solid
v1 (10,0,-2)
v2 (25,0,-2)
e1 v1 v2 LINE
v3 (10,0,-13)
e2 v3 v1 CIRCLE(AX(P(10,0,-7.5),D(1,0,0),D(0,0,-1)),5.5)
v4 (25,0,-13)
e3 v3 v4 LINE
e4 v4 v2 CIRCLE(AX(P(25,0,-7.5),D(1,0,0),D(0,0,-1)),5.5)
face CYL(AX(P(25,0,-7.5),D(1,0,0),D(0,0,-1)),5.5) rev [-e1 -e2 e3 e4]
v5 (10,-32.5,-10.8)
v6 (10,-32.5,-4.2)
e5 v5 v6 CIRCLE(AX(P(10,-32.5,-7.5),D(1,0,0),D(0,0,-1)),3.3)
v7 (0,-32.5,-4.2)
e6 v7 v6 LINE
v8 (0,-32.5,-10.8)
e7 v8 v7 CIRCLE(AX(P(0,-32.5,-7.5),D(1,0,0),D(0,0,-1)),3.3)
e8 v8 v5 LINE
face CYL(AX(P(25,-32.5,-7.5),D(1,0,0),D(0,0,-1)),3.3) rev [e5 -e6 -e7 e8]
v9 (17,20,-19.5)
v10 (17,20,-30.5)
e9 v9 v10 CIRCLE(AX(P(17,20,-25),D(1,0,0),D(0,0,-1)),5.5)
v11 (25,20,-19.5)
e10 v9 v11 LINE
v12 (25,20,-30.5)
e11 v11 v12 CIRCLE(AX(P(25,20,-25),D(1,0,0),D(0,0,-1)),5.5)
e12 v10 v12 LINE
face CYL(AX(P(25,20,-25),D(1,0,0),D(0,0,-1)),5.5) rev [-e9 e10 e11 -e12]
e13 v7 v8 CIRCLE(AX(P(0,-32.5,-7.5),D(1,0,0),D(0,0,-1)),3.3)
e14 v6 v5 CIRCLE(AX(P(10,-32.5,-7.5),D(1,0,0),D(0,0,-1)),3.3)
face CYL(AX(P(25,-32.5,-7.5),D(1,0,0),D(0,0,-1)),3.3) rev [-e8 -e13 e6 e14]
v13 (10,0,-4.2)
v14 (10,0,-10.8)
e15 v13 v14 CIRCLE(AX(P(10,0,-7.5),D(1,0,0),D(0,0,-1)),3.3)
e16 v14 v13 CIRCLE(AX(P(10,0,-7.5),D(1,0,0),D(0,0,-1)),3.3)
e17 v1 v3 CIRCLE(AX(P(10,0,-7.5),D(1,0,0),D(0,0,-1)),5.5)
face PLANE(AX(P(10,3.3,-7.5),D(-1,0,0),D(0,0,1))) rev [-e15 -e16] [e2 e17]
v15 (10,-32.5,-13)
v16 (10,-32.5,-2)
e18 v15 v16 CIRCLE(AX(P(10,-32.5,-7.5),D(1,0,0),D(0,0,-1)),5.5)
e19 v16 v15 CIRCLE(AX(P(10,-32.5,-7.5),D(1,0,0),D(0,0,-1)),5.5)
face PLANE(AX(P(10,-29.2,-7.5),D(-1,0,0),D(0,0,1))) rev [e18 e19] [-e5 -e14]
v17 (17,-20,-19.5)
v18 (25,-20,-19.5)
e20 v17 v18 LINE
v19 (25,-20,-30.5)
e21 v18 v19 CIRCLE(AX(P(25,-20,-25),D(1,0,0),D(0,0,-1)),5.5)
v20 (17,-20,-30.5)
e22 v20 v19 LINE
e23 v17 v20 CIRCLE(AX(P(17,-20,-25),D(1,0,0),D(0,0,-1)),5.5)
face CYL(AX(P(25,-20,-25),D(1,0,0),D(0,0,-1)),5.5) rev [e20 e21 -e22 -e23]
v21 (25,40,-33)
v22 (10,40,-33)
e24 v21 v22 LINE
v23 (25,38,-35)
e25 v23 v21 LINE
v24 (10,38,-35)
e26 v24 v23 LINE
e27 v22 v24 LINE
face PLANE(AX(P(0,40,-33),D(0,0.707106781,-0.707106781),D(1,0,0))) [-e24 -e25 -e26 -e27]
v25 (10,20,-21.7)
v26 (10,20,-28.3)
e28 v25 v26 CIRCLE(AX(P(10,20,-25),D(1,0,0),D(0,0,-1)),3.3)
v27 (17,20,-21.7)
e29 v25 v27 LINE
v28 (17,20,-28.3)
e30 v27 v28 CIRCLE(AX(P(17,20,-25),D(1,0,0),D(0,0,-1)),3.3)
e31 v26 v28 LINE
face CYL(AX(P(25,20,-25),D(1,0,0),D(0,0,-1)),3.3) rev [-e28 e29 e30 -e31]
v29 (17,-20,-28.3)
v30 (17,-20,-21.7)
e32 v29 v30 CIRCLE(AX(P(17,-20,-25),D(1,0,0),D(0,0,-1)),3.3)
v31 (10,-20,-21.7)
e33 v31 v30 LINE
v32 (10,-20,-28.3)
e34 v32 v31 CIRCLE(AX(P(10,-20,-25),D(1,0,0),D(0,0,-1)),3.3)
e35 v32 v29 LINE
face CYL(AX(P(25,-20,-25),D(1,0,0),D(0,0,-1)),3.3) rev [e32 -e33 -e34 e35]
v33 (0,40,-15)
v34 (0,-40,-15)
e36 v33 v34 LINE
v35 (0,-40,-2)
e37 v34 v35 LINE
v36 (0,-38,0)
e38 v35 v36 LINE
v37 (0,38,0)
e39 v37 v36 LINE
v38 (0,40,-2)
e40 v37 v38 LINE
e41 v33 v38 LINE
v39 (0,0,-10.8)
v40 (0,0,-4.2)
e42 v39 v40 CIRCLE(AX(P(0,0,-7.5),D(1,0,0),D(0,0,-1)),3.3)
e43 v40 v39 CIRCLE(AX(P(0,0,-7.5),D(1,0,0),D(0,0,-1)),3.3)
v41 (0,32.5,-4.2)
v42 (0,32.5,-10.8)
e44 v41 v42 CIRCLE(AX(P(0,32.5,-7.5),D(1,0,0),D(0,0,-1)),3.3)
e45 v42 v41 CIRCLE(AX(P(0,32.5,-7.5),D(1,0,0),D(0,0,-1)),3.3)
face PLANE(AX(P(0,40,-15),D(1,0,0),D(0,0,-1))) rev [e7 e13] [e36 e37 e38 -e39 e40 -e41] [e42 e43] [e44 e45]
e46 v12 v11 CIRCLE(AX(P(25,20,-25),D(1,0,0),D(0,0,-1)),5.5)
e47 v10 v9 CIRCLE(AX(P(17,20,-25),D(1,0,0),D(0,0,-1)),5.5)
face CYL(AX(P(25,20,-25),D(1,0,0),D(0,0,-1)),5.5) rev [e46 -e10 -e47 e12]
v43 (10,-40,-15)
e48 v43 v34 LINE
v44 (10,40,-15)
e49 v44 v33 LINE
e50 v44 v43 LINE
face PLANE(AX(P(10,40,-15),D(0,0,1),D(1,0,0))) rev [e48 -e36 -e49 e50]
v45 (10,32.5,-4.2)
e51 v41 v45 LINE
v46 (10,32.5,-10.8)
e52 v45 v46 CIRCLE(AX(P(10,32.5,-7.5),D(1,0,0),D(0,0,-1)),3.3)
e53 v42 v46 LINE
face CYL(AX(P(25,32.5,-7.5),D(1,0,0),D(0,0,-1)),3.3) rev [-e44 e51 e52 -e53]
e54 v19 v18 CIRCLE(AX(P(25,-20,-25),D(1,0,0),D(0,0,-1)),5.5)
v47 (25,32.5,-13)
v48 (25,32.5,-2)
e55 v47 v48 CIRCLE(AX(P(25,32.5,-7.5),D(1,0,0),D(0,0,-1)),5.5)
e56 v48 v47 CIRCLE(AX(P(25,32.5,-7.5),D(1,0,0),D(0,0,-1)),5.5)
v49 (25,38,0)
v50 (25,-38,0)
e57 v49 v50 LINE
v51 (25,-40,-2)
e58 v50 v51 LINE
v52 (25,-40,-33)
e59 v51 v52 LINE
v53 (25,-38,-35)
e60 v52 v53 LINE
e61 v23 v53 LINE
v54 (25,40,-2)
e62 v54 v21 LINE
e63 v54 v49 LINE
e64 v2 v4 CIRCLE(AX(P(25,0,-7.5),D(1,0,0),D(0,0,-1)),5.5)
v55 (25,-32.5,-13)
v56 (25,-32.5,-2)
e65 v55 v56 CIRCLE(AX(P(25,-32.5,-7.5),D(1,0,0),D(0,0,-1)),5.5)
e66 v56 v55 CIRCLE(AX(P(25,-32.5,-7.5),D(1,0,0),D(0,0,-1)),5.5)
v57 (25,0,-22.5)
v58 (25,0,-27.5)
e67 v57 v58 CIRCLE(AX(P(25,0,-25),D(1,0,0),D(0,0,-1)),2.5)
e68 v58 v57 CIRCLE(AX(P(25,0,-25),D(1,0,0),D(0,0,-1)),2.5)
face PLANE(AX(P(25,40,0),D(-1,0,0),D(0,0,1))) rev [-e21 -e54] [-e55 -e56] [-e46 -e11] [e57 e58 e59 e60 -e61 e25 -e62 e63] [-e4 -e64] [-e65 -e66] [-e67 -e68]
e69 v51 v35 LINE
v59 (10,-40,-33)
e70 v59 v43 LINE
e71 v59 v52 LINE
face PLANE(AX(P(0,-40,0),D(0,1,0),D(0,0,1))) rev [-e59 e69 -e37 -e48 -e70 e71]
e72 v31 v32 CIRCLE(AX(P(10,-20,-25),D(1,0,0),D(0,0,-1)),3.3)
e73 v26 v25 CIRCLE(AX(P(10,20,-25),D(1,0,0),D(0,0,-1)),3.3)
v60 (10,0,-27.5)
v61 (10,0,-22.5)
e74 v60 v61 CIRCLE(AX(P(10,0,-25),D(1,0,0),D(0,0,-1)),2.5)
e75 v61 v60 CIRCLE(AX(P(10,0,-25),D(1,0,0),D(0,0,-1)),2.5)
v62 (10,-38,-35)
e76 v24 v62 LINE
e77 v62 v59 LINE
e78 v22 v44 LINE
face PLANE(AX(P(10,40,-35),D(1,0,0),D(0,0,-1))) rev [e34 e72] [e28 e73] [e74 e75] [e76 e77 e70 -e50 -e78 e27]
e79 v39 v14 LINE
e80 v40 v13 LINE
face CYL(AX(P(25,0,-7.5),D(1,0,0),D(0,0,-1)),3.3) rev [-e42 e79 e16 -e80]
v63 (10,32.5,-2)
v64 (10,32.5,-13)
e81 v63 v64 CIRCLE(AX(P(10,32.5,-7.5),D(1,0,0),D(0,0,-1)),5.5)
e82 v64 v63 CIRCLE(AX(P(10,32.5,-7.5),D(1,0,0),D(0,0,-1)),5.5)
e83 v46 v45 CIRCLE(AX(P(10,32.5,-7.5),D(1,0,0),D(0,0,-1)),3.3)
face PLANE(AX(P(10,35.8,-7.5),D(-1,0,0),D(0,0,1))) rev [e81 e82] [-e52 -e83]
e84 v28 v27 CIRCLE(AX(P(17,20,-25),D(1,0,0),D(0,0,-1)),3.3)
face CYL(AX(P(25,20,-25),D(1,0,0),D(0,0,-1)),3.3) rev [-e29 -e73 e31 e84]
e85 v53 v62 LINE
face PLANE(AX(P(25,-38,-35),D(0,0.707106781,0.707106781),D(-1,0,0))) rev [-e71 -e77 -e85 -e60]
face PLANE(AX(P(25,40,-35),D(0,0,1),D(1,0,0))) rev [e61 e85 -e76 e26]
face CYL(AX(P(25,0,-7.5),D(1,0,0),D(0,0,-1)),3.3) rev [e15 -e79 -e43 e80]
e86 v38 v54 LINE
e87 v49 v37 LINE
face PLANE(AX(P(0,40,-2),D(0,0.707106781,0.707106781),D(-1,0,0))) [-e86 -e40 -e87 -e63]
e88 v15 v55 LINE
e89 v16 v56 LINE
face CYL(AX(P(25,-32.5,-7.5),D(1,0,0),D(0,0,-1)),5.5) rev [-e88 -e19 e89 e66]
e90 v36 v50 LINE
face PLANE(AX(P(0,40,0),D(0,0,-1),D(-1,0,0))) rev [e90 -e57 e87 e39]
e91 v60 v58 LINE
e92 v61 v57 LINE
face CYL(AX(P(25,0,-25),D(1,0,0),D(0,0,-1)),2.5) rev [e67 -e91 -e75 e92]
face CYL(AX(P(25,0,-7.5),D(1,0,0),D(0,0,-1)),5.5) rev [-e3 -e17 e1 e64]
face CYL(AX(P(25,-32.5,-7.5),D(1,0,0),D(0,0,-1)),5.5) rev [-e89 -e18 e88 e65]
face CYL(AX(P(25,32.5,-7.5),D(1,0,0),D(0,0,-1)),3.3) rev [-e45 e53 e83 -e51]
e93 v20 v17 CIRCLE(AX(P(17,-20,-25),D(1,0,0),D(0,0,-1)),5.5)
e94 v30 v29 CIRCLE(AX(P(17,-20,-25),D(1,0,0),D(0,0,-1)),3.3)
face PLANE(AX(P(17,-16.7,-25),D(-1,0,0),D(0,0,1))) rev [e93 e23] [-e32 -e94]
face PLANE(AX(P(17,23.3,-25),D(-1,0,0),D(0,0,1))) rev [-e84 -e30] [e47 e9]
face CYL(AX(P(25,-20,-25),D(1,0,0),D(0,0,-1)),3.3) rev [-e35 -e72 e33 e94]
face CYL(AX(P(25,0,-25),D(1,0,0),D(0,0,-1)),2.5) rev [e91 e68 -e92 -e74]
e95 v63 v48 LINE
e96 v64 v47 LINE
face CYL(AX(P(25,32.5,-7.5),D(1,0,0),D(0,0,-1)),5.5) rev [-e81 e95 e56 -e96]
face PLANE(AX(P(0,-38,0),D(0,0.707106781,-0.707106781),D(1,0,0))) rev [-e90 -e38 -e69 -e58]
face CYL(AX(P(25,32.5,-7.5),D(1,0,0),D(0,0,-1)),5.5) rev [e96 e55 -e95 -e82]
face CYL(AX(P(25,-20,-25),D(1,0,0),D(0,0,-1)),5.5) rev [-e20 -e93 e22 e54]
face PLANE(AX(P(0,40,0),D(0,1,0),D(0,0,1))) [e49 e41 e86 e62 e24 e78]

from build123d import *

# Parameters (mm, degrees)
EXTRUDE_1_DEPTH              = 40
CHAMFER_1_SIZE               = 2
HOLE_WIZARD_M6_1_D           = 6.6
HOLE_WIZARD_M6_1_CBORE_D     = 11
HOLE_WIZARD_M6_1_CBORE_DEPTH = 15
HOLE_WIZARD_M6_1_2_D         = 5
HOLE_WIZARD_M6_2_D           = 6.6
HOLE_WIZARD_M6_2_CBORE_D     = 11
HOLE_WIZARD_M6_2_CBORE_DEPTH = 8


with BuildPart() as part:
    # 草图1 → 凸台-拉伸1 (new, symmetric)
    with BuildSketch(Plane(origin=(0, 0, 0), x_dir=(1, 0, 0), z_dir=(0, 1, 0))):
        Polygon((0, 0), (25, 0), (25, 35), (10, 35), (10, 15), (0, 15), align=None)
    extrude(amount=EXTRUDE_1_DEPTH, both=True)

    # 倒角1
    chamfer_1_edges = [part.edges().sort_by_distance(p)[0] for p in [
        (17.5, 40, -35),
        (17.5, -40, -35),
        (12.5, -40, 0),
        (12.5, 40, 0),
    ]]
    chamfer(chamfer_1_edges, length=CHAMFER_1_SIZE)

    # Hole Wizard M6 _1 (through all)
    with Locations(Plane(origin=(25, 0, 0), x_dir=(0, 0, -1), z_dir=(1, 0, 0))):
        with Locations((7.5, 32.5), (7.5, 0), (7.5, -32.5)):
            CounterBoreHole(HOLE_WIZARD_M6_1_D / 2, HOLE_WIZARD_M6_1_CBORE_D / 2, HOLE_WIZARD_M6_1_CBORE_DEPTH)

    # Hole Wizard M6 _1 2 (through all)
    with Locations(Plane(origin=(25, 0, 0), x_dir=(0, 0, -1), z_dir=(1, 0, 0))):
        with Locations((25, 0)):
            Hole(HOLE_WIZARD_M6_1_2_D / 2)

    # M6 六角圆柱头螺钉的柱形沉头孔2 (through all)
    with Locations(Plane(origin=(25, 0, 0), x_dir=(0, 0, -1), z_dir=(1, 0, 0))):
        with Locations((25, 20), (25, -20)):
            CounterBoreHole(HOLE_WIZARD_M6_2_D / 2, HOLE_WIZARD_M6_2_CBORE_D / 2, HOLE_WIZARD_M6_2_CBORE_DEPTH)


solid = part.part
